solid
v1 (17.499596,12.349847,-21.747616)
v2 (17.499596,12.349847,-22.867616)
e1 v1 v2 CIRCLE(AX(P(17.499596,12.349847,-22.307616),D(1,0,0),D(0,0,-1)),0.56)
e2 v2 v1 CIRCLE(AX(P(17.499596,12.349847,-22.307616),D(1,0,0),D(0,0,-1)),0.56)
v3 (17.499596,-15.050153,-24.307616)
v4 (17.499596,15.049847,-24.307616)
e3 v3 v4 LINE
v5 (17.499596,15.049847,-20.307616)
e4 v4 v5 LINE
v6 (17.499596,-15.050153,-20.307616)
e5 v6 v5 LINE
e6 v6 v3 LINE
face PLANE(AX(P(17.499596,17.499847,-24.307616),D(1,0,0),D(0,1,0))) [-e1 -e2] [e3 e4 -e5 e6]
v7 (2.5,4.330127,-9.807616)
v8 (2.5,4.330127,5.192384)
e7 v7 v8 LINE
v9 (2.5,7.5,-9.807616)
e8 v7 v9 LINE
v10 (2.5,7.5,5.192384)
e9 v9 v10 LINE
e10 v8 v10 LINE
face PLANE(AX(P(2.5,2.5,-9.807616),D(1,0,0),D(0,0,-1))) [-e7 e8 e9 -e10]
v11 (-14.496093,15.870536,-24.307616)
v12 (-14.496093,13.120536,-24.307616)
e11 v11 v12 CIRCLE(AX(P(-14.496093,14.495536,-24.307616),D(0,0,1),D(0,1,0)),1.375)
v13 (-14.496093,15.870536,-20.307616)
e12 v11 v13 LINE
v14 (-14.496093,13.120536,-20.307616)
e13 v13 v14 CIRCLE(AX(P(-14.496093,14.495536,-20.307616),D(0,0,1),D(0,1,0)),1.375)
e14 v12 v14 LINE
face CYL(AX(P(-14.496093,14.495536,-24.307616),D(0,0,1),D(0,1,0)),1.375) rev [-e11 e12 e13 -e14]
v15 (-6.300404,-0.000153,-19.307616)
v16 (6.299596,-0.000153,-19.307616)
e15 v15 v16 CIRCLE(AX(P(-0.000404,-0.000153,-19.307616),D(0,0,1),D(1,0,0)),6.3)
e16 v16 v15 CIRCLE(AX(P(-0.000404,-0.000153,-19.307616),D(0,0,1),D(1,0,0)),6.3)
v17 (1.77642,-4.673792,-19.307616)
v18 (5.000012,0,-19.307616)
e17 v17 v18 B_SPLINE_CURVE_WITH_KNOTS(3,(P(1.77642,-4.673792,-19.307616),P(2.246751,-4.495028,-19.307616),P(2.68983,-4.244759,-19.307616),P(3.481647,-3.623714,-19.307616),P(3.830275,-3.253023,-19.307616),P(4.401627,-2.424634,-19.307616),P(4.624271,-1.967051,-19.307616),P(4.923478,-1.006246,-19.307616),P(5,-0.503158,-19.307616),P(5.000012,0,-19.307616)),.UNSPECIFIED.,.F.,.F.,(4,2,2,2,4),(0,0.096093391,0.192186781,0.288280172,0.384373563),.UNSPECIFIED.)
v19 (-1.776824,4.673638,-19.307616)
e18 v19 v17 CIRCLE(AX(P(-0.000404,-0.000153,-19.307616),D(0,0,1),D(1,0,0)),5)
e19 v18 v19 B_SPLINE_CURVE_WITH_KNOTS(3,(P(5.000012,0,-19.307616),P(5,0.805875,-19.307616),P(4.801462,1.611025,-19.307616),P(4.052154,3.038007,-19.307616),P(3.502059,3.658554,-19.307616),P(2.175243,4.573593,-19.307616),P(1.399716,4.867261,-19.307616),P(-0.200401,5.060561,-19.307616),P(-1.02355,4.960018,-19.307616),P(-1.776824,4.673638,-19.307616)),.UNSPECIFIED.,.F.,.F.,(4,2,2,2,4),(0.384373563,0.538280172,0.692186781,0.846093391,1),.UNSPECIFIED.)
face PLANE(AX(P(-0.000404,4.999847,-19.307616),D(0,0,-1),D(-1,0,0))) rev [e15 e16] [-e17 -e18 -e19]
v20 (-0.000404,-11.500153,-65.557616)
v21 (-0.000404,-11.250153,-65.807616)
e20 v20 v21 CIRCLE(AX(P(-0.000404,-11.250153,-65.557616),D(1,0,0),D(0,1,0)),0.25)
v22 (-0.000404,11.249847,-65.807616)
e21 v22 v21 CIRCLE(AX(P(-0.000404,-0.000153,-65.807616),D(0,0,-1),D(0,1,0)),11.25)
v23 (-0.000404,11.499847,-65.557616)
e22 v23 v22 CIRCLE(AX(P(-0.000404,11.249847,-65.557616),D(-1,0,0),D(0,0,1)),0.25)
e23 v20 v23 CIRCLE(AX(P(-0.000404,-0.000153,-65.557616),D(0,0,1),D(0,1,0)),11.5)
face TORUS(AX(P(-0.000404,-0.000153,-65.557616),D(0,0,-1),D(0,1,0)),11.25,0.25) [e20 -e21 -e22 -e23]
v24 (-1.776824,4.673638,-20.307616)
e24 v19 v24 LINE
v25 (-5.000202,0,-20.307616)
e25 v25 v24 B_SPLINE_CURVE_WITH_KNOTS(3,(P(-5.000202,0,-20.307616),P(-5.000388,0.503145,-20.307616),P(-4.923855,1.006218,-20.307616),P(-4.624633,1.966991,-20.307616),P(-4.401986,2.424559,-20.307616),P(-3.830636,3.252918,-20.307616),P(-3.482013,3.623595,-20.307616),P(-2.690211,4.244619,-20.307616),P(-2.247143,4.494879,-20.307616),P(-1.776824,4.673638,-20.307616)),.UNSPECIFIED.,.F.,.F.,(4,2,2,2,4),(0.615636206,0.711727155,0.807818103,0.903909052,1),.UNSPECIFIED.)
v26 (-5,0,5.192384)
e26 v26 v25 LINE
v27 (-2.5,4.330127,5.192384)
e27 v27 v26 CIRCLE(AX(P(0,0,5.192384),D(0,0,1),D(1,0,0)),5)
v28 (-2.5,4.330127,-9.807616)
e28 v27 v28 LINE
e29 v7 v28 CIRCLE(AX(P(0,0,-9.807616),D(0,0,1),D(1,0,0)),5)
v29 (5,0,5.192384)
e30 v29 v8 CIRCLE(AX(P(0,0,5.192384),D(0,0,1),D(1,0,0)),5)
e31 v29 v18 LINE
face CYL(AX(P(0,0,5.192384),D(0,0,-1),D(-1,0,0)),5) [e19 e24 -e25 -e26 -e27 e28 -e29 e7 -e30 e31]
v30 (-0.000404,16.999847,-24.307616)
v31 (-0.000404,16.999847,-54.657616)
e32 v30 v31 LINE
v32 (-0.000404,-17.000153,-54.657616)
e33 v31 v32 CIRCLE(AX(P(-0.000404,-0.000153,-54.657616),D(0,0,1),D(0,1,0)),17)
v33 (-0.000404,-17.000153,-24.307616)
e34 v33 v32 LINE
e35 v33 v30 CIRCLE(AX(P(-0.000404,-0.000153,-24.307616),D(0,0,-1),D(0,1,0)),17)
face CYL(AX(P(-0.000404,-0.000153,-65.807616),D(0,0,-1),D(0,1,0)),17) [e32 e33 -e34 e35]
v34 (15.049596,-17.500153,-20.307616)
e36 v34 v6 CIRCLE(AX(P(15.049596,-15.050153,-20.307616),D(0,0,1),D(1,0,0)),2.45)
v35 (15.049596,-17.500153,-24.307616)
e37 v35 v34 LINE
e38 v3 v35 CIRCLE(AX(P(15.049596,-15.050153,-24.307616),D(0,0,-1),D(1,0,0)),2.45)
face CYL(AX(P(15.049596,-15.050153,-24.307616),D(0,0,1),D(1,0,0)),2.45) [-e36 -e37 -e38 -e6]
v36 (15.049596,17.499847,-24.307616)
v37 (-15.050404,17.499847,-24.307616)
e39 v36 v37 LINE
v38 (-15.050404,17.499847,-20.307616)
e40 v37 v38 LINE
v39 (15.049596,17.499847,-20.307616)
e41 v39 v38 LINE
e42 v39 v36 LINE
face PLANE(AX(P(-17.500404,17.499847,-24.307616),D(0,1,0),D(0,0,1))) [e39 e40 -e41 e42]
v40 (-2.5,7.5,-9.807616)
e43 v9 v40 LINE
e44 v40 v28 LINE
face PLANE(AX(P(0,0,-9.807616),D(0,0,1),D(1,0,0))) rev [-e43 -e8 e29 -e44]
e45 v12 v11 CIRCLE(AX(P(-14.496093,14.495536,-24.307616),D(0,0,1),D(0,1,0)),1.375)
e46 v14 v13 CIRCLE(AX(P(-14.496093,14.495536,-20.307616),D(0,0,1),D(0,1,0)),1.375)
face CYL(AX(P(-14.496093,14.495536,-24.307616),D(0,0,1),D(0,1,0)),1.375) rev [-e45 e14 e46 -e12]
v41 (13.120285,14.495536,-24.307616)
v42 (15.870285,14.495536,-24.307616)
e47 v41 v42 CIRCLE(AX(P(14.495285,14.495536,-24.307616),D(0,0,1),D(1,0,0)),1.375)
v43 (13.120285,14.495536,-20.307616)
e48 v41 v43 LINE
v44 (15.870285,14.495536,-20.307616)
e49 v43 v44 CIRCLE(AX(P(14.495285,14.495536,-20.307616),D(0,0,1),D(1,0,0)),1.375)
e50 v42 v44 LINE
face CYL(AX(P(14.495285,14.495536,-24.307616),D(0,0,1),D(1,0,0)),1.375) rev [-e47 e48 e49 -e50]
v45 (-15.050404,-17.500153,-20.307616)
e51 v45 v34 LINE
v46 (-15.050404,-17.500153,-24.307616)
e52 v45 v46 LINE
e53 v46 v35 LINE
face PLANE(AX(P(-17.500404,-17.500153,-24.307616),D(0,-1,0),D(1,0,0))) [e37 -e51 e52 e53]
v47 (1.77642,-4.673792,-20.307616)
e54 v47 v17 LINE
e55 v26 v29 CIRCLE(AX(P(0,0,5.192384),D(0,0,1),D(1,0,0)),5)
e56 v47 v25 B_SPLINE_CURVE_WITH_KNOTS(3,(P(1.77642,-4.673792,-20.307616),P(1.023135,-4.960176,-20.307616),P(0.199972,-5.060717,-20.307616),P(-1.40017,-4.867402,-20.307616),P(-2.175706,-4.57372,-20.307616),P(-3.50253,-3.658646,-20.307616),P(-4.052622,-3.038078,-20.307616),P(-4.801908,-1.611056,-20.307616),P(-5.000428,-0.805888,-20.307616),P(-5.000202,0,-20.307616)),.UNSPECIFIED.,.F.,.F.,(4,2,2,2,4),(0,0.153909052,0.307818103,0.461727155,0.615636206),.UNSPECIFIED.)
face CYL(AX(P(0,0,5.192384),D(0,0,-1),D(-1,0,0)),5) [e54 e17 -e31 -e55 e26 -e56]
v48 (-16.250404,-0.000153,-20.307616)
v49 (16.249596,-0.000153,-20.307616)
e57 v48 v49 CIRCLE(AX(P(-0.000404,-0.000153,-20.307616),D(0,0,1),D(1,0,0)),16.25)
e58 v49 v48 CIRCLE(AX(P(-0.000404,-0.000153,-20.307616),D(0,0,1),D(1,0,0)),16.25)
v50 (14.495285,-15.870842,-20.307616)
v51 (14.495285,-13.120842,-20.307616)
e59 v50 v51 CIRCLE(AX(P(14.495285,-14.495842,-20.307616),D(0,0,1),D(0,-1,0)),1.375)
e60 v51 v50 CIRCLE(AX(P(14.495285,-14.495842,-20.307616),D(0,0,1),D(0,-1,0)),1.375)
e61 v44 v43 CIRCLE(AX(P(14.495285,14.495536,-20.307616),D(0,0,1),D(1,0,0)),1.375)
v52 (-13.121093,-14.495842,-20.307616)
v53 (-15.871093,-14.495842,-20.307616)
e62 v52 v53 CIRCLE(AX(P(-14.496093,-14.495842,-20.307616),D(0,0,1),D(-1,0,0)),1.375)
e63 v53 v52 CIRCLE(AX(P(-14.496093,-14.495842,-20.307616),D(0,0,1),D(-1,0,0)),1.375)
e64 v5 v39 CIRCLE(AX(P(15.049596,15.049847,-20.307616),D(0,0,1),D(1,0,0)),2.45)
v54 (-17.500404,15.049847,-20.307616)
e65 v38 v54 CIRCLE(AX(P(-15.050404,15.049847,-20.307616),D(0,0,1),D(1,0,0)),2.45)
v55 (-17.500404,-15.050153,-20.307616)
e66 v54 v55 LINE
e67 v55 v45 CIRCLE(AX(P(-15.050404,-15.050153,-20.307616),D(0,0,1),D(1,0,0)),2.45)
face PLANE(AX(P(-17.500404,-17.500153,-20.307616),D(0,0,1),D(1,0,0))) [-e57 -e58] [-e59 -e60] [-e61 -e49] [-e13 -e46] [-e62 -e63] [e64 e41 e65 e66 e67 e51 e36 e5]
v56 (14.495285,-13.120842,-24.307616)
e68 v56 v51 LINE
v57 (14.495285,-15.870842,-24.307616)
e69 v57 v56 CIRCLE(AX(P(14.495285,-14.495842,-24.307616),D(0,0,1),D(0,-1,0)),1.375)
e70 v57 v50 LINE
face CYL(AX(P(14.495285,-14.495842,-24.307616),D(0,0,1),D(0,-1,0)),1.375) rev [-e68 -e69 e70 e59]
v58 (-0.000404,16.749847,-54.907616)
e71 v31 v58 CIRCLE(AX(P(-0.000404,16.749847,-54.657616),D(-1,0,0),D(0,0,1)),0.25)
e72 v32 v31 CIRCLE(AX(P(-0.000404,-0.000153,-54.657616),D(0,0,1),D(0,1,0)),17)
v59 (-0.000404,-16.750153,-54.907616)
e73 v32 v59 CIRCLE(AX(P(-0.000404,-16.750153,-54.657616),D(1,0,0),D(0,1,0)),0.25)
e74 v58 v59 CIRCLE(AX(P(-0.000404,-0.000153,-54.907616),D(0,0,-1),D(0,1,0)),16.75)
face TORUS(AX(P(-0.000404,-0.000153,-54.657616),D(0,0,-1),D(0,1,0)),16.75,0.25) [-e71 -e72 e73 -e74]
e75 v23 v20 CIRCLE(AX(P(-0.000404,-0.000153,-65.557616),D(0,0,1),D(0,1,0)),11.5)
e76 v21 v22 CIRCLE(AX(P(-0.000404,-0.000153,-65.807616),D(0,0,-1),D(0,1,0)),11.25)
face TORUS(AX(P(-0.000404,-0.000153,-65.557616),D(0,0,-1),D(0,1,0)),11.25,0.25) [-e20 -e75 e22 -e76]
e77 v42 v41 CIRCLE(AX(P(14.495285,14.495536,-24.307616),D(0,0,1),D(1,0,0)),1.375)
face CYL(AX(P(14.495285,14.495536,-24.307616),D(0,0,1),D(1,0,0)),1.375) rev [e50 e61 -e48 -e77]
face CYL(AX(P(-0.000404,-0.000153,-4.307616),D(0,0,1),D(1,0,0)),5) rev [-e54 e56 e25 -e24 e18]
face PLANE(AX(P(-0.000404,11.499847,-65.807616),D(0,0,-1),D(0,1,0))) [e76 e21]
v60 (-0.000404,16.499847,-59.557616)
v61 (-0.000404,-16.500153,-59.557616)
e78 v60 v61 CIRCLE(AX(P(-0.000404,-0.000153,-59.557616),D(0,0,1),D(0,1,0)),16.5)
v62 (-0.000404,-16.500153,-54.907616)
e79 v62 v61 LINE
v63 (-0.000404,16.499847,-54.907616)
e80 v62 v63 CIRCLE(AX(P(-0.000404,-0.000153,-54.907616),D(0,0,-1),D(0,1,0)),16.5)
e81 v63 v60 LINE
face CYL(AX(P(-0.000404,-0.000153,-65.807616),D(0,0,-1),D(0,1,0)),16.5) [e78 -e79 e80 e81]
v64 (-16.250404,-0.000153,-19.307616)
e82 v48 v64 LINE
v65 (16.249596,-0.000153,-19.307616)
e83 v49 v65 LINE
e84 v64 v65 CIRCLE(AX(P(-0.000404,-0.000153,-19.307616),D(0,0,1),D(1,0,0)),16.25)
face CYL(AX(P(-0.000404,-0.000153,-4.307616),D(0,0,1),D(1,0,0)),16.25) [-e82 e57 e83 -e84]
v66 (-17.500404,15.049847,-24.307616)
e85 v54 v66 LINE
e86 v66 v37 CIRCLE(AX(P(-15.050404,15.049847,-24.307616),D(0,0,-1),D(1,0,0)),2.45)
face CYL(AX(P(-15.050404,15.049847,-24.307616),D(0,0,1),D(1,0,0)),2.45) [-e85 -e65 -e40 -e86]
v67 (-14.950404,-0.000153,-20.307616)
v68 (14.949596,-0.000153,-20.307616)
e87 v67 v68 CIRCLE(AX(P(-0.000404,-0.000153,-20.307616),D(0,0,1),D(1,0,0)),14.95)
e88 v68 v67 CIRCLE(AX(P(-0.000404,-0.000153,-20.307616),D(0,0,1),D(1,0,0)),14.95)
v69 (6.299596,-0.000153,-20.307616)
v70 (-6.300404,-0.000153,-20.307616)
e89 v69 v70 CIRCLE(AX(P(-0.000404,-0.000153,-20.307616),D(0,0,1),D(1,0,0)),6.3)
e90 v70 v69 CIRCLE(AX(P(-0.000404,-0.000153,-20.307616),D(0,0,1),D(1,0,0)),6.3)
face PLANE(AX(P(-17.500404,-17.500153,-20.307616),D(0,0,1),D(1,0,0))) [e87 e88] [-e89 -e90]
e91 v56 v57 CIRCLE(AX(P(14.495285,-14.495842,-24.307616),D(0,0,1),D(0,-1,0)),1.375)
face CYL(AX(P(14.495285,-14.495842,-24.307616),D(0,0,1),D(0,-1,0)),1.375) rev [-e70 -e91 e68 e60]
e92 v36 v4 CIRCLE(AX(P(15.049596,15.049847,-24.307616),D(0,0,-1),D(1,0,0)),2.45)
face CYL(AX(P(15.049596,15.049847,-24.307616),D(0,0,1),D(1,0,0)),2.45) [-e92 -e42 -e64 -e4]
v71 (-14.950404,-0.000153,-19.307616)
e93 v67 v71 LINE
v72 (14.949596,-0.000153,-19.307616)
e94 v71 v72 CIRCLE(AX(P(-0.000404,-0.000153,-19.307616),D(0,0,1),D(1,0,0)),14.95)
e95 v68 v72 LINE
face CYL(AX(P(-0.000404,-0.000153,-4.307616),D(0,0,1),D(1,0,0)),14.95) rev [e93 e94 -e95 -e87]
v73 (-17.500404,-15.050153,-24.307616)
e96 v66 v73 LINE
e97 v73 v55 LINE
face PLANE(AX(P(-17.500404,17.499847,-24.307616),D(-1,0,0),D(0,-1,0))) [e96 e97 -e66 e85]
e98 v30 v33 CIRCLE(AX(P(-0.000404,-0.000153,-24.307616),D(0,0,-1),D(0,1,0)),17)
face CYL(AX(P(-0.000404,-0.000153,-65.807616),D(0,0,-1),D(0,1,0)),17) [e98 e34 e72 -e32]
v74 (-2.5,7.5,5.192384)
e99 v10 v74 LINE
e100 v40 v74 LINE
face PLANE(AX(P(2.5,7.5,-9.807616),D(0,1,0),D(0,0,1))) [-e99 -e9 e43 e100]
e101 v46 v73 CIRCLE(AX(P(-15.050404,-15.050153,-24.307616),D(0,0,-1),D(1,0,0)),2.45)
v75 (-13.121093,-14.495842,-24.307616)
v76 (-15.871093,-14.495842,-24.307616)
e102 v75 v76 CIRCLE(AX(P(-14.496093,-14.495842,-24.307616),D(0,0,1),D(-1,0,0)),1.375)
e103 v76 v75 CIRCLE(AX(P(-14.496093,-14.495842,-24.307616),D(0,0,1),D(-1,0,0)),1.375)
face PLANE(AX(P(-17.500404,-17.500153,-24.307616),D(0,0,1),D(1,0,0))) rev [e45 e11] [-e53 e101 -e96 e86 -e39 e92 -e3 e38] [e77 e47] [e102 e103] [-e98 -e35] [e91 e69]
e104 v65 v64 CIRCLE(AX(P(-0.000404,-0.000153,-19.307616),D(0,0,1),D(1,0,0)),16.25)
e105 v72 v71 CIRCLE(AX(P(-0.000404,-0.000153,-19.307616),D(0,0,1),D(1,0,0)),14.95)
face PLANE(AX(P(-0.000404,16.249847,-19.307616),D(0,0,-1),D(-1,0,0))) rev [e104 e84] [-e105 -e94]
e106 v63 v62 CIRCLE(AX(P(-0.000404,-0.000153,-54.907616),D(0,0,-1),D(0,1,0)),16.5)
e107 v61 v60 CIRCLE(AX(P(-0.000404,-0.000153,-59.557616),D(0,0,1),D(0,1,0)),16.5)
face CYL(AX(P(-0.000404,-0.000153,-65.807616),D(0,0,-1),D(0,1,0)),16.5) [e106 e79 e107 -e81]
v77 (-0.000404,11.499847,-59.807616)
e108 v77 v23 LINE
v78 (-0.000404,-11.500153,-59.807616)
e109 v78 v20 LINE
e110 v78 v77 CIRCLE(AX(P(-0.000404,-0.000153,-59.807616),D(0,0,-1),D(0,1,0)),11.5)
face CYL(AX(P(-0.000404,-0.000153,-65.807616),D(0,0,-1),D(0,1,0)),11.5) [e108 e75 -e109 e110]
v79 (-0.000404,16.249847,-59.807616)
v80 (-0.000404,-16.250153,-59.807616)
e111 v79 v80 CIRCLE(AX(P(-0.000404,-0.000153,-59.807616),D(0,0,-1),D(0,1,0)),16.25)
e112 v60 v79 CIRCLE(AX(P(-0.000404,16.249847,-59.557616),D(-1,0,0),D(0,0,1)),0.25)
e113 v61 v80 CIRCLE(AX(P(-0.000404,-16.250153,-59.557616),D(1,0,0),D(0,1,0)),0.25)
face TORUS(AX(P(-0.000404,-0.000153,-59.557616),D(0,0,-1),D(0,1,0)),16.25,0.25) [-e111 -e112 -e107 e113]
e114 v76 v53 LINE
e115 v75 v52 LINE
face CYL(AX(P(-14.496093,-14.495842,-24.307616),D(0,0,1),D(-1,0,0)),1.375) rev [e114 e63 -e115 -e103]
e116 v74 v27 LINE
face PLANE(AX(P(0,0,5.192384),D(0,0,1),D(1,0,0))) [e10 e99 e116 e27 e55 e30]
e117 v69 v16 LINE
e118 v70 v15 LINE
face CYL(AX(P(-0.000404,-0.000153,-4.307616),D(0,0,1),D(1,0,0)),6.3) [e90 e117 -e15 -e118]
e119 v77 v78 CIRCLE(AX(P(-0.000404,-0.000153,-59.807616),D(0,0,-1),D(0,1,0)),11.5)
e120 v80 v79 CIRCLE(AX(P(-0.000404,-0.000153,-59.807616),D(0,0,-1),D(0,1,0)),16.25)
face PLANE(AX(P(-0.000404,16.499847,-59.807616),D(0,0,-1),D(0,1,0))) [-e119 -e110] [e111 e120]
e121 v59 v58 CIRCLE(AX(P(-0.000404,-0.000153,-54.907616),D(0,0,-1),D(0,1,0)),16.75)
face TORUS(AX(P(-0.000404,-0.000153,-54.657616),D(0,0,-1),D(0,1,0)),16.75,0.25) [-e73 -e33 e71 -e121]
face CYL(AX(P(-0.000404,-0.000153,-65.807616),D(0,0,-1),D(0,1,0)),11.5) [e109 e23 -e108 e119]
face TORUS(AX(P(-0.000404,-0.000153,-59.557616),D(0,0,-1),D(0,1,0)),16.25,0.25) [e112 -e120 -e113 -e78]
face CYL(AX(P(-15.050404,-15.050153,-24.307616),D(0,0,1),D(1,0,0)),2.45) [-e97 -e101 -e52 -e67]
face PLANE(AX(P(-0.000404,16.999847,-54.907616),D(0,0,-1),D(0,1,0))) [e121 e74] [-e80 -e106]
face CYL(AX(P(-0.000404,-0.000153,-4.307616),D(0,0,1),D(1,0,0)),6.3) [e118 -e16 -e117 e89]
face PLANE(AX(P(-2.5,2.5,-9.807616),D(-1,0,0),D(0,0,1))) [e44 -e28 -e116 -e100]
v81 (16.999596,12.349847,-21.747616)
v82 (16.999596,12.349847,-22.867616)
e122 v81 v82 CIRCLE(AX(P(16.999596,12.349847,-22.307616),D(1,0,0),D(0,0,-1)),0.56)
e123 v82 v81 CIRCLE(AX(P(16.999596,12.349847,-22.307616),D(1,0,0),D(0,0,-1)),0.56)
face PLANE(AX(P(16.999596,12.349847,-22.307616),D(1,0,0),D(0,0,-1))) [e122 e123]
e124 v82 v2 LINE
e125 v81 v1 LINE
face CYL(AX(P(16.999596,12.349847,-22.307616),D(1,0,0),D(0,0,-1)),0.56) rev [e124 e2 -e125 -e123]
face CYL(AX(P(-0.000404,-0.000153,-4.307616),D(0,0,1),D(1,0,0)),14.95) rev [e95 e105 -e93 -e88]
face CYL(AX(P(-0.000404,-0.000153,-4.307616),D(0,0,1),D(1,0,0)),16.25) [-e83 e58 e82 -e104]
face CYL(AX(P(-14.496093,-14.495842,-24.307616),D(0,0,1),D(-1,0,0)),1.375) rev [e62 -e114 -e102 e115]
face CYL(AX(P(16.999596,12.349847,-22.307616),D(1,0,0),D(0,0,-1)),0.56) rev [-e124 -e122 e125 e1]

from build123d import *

# Parameters (mm, degrees)
SKETCH_3_W                  = 70
SKETCH_3_H                  = 70
EXTRUDE_1_DEPTH             = 8
SKETCH_5_W                  = 32
SKETCH_5_H                  = 4
SKETCH_5_W_2                = 2
SKETCH_5_H_2                = 2.6
SKETCH_4_R                  = 2.75
CUT_EXTRUDE_1_DEPTH         = 8
PATTERN_CIRCULAR_1_COUNT    = 4
FILLET_1_R                  = 4.9
SKETCH_7_R                  = 1.12
CUT_EXTRUDE_2_DEPTH         = 1
CUT_EXTRUDE_START           = -25
CUT_EXTRUDE_7_DEPTH         = 25
CHAMFER_2_SIZE              = 0.38
SKETCH_35_R                 = 6
EXTRUDE_7_DEPTH             = 4
FILLET_4_R                  = 0.5
SCALE_1_SCALE               = 0.5
EXTRUDE_8_REACH             = 68.293
SKETCH_37_R                 = 5
EXTRUDE_8_DIRECTION_2_DEPTH = 9.5
SKETCH_38_W                 = 5
SKETCH_38_H                 = 5
EXTRUDE_9_DEPTH             = 15


with BuildPart() as part:
    # 草图3 → 凸台-拉伸1 (new body)
    with BuildSketch(Plane.XY):
        Rectangle(SKETCH_3_W, SKETCH_3_H)
    extrude(amount=-EXTRUDE_1_DEPTH)

    # 草图5 → 旋转1 (revolve)
    with BuildSketch(Plane(origin=(0, 0, 0), x_dir=(0, 0, -1), z_dir=(1, 0, 0)), mode=Mode.PRIVATE) as revolve_1_sk:
        with Locations((-16, 2)):
            Rectangle(SKETCH_5_W, SKETCH_5_H)
        with Locations((-1, 31.2)):
            Rectangle(SKETCH_5_W_2, SKETCH_5_H_2)
        with Locations((-1, 11.3)):
            Rectangle(SKETCH_5_W_2, SKETCH_5_H_2)
    revolve(revolve_1_sk.sketch.rotate(Axis((0, 0, 32), (0, 0, -1)), 90), axis=Axis((0, 0, 32), (0, 0, -1)))

    # 草图4 → 切除-拉伸1 (cut)
    with BuildSketch(Plane.XY):
        with Locations((28.991378029, 28.991378029)):
            Circle(SKETCH_4_R)
    cut_extrude_1 = extrude(amount=-CUT_EXTRUDE_1_DEPTH, mode=Mode.SUBTRACT)

    # 阵列(圆周)1: 切除-拉伸1 ×4 about axis
    pattern_circular_1_axis = Axis((0, 0, 0), (0, 0, 1))
    for i in range(1, PATTERN_CIRCULAR_1_COUNT):
        add(cut_extrude_1.rotate(pattern_circular_1_axis, i * 360 / PATTERN_CIRCULAR_1_COUNT), mode=Mode.SUBTRACT)

    # 圆角1
    fillet_1_edges = [part.edges().sort_by_distance(p)[0] for p in [
        (-35, 35, -4),
        (35, 35, -4),
        (35, -35, -4),
        (-35, -35, -4),
    ]]
    fillet(fillet_1_edges, radius=FILLET_1_R)

    # 草图7 → 切除-拉伸2 (cut)
    with BuildSketch(Plane(origin=(35, 0, 0), x_dir=(0, 0, -1), z_dir=(1, 0, 0))):
        with Locations((4, 24.7)):
            Circle(SKETCH_7_R)
    extrude(amount=-CUT_EXTRUDE_2_DEPTH, mode=Mode.SUBTRACT)

    # 草图31 → 切除-拉伸7 (cut)
    with BuildSketch(Plane.XY.offset(32).offset(CUT_EXTRUDE_START)):
        with BuildLine():
            Line((3.5, 1.936491673), (3.5, -1.936491673))
            ThreePointArc((3.5, -1.936491673), (4, 0), (3.5, 1.936491673))
        make_face()
    extrude(amount=CUT_EXTRUDE_7_DEPTH, mode=Mode.SUBTRACT)

    # 倒角2
    chamfer_2_edges = [part.edges().sort_by_distance(p)[0] for p in [
        (-4, 0, 32),
    ]]
    chamfer(chamfer_2_edges, length=CHAMFER_2_SIZE)

    # 草图35 → 凸台-拉伸7 (add)
    with BuildSketch(Plane.XY):
        Circle(SKETCH_35_R)
    extrude(amount=EXTRUDE_7_DEPTH)

    # 草图8 → 旋转3 (revolve)
    with BuildSketch(Plane(origin=(0, 0, 0), x_dir=(0, 0, -1), z_dir=(1, 0, 0))):
        Polygon((8, 34), (69.2, 34), (69.2, 33), (79, 33), (79, 23), (91, 23), (91, 0), (8, 0), align=None)
    revolve(axis=Axis((0, 0, -91), (0, 0, 1)))

    # 圆角4
    fillet_4_edges = [part.edges().sort_by_distance(p)[0] for p in [
        (0, -34, -69.2),
        (0, -33, -79),
        (0, -23, -91),
    ]]
    fillet(fillet_4_edges, radius=FILLET_4_R)


with BuildPart() as part_1:
    # 缩放比例1: scaled about (-0.000807306, -0.000306882, -40.615231306)
    add(part.part.scale(SCALE_1_SCALE).moved(Location((-0.000403653, -0.000153441, -20.307615653))))

    # 草图37 → 凸台-拉伸8 (add, up to next)
    with BuildSketch(Plane.XY.offset(-4.307615654), mode=Mode.PRIVATE) as extrude_8_sk1:
        with Locations(Location((0, 0, 0), (0, 0, 110.815805109))):
            Circle(SKETCH_37_R)
    extrude_8_tool1 = extrude(extrude_8_sk1.sketch, amount=-EXTRUDE_8_REACH, mode=Mode.PRIVATE) - part_1.part
    add(extrude_8_tool1.solids().sort_by_distance((0, 0, -4.307616))[0])

    # 草图37 → 凸台-拉伸8 direction 2 (add)
    with BuildSketch(Plane.XY.offset(-4.307615654)):
        with Locations(Location((0, 0, 0), (0, 0, 110.815805109))):
            Circle(SKETCH_37_R)
    extrude(amount=EXTRUDE_8_DIRECTION_2_DEPTH)

    # 草图38 → 凸台-拉伸9 (add)
    with BuildSketch(Plane.XY.offset(5.192384346)):
        with Locations((0, 5)):
            Rectangle(SKETCH_38_W, SKETCH_38_H)
    extrude(amount=-EXTRUDE_9_DEPTH)


solid = part_1.part
